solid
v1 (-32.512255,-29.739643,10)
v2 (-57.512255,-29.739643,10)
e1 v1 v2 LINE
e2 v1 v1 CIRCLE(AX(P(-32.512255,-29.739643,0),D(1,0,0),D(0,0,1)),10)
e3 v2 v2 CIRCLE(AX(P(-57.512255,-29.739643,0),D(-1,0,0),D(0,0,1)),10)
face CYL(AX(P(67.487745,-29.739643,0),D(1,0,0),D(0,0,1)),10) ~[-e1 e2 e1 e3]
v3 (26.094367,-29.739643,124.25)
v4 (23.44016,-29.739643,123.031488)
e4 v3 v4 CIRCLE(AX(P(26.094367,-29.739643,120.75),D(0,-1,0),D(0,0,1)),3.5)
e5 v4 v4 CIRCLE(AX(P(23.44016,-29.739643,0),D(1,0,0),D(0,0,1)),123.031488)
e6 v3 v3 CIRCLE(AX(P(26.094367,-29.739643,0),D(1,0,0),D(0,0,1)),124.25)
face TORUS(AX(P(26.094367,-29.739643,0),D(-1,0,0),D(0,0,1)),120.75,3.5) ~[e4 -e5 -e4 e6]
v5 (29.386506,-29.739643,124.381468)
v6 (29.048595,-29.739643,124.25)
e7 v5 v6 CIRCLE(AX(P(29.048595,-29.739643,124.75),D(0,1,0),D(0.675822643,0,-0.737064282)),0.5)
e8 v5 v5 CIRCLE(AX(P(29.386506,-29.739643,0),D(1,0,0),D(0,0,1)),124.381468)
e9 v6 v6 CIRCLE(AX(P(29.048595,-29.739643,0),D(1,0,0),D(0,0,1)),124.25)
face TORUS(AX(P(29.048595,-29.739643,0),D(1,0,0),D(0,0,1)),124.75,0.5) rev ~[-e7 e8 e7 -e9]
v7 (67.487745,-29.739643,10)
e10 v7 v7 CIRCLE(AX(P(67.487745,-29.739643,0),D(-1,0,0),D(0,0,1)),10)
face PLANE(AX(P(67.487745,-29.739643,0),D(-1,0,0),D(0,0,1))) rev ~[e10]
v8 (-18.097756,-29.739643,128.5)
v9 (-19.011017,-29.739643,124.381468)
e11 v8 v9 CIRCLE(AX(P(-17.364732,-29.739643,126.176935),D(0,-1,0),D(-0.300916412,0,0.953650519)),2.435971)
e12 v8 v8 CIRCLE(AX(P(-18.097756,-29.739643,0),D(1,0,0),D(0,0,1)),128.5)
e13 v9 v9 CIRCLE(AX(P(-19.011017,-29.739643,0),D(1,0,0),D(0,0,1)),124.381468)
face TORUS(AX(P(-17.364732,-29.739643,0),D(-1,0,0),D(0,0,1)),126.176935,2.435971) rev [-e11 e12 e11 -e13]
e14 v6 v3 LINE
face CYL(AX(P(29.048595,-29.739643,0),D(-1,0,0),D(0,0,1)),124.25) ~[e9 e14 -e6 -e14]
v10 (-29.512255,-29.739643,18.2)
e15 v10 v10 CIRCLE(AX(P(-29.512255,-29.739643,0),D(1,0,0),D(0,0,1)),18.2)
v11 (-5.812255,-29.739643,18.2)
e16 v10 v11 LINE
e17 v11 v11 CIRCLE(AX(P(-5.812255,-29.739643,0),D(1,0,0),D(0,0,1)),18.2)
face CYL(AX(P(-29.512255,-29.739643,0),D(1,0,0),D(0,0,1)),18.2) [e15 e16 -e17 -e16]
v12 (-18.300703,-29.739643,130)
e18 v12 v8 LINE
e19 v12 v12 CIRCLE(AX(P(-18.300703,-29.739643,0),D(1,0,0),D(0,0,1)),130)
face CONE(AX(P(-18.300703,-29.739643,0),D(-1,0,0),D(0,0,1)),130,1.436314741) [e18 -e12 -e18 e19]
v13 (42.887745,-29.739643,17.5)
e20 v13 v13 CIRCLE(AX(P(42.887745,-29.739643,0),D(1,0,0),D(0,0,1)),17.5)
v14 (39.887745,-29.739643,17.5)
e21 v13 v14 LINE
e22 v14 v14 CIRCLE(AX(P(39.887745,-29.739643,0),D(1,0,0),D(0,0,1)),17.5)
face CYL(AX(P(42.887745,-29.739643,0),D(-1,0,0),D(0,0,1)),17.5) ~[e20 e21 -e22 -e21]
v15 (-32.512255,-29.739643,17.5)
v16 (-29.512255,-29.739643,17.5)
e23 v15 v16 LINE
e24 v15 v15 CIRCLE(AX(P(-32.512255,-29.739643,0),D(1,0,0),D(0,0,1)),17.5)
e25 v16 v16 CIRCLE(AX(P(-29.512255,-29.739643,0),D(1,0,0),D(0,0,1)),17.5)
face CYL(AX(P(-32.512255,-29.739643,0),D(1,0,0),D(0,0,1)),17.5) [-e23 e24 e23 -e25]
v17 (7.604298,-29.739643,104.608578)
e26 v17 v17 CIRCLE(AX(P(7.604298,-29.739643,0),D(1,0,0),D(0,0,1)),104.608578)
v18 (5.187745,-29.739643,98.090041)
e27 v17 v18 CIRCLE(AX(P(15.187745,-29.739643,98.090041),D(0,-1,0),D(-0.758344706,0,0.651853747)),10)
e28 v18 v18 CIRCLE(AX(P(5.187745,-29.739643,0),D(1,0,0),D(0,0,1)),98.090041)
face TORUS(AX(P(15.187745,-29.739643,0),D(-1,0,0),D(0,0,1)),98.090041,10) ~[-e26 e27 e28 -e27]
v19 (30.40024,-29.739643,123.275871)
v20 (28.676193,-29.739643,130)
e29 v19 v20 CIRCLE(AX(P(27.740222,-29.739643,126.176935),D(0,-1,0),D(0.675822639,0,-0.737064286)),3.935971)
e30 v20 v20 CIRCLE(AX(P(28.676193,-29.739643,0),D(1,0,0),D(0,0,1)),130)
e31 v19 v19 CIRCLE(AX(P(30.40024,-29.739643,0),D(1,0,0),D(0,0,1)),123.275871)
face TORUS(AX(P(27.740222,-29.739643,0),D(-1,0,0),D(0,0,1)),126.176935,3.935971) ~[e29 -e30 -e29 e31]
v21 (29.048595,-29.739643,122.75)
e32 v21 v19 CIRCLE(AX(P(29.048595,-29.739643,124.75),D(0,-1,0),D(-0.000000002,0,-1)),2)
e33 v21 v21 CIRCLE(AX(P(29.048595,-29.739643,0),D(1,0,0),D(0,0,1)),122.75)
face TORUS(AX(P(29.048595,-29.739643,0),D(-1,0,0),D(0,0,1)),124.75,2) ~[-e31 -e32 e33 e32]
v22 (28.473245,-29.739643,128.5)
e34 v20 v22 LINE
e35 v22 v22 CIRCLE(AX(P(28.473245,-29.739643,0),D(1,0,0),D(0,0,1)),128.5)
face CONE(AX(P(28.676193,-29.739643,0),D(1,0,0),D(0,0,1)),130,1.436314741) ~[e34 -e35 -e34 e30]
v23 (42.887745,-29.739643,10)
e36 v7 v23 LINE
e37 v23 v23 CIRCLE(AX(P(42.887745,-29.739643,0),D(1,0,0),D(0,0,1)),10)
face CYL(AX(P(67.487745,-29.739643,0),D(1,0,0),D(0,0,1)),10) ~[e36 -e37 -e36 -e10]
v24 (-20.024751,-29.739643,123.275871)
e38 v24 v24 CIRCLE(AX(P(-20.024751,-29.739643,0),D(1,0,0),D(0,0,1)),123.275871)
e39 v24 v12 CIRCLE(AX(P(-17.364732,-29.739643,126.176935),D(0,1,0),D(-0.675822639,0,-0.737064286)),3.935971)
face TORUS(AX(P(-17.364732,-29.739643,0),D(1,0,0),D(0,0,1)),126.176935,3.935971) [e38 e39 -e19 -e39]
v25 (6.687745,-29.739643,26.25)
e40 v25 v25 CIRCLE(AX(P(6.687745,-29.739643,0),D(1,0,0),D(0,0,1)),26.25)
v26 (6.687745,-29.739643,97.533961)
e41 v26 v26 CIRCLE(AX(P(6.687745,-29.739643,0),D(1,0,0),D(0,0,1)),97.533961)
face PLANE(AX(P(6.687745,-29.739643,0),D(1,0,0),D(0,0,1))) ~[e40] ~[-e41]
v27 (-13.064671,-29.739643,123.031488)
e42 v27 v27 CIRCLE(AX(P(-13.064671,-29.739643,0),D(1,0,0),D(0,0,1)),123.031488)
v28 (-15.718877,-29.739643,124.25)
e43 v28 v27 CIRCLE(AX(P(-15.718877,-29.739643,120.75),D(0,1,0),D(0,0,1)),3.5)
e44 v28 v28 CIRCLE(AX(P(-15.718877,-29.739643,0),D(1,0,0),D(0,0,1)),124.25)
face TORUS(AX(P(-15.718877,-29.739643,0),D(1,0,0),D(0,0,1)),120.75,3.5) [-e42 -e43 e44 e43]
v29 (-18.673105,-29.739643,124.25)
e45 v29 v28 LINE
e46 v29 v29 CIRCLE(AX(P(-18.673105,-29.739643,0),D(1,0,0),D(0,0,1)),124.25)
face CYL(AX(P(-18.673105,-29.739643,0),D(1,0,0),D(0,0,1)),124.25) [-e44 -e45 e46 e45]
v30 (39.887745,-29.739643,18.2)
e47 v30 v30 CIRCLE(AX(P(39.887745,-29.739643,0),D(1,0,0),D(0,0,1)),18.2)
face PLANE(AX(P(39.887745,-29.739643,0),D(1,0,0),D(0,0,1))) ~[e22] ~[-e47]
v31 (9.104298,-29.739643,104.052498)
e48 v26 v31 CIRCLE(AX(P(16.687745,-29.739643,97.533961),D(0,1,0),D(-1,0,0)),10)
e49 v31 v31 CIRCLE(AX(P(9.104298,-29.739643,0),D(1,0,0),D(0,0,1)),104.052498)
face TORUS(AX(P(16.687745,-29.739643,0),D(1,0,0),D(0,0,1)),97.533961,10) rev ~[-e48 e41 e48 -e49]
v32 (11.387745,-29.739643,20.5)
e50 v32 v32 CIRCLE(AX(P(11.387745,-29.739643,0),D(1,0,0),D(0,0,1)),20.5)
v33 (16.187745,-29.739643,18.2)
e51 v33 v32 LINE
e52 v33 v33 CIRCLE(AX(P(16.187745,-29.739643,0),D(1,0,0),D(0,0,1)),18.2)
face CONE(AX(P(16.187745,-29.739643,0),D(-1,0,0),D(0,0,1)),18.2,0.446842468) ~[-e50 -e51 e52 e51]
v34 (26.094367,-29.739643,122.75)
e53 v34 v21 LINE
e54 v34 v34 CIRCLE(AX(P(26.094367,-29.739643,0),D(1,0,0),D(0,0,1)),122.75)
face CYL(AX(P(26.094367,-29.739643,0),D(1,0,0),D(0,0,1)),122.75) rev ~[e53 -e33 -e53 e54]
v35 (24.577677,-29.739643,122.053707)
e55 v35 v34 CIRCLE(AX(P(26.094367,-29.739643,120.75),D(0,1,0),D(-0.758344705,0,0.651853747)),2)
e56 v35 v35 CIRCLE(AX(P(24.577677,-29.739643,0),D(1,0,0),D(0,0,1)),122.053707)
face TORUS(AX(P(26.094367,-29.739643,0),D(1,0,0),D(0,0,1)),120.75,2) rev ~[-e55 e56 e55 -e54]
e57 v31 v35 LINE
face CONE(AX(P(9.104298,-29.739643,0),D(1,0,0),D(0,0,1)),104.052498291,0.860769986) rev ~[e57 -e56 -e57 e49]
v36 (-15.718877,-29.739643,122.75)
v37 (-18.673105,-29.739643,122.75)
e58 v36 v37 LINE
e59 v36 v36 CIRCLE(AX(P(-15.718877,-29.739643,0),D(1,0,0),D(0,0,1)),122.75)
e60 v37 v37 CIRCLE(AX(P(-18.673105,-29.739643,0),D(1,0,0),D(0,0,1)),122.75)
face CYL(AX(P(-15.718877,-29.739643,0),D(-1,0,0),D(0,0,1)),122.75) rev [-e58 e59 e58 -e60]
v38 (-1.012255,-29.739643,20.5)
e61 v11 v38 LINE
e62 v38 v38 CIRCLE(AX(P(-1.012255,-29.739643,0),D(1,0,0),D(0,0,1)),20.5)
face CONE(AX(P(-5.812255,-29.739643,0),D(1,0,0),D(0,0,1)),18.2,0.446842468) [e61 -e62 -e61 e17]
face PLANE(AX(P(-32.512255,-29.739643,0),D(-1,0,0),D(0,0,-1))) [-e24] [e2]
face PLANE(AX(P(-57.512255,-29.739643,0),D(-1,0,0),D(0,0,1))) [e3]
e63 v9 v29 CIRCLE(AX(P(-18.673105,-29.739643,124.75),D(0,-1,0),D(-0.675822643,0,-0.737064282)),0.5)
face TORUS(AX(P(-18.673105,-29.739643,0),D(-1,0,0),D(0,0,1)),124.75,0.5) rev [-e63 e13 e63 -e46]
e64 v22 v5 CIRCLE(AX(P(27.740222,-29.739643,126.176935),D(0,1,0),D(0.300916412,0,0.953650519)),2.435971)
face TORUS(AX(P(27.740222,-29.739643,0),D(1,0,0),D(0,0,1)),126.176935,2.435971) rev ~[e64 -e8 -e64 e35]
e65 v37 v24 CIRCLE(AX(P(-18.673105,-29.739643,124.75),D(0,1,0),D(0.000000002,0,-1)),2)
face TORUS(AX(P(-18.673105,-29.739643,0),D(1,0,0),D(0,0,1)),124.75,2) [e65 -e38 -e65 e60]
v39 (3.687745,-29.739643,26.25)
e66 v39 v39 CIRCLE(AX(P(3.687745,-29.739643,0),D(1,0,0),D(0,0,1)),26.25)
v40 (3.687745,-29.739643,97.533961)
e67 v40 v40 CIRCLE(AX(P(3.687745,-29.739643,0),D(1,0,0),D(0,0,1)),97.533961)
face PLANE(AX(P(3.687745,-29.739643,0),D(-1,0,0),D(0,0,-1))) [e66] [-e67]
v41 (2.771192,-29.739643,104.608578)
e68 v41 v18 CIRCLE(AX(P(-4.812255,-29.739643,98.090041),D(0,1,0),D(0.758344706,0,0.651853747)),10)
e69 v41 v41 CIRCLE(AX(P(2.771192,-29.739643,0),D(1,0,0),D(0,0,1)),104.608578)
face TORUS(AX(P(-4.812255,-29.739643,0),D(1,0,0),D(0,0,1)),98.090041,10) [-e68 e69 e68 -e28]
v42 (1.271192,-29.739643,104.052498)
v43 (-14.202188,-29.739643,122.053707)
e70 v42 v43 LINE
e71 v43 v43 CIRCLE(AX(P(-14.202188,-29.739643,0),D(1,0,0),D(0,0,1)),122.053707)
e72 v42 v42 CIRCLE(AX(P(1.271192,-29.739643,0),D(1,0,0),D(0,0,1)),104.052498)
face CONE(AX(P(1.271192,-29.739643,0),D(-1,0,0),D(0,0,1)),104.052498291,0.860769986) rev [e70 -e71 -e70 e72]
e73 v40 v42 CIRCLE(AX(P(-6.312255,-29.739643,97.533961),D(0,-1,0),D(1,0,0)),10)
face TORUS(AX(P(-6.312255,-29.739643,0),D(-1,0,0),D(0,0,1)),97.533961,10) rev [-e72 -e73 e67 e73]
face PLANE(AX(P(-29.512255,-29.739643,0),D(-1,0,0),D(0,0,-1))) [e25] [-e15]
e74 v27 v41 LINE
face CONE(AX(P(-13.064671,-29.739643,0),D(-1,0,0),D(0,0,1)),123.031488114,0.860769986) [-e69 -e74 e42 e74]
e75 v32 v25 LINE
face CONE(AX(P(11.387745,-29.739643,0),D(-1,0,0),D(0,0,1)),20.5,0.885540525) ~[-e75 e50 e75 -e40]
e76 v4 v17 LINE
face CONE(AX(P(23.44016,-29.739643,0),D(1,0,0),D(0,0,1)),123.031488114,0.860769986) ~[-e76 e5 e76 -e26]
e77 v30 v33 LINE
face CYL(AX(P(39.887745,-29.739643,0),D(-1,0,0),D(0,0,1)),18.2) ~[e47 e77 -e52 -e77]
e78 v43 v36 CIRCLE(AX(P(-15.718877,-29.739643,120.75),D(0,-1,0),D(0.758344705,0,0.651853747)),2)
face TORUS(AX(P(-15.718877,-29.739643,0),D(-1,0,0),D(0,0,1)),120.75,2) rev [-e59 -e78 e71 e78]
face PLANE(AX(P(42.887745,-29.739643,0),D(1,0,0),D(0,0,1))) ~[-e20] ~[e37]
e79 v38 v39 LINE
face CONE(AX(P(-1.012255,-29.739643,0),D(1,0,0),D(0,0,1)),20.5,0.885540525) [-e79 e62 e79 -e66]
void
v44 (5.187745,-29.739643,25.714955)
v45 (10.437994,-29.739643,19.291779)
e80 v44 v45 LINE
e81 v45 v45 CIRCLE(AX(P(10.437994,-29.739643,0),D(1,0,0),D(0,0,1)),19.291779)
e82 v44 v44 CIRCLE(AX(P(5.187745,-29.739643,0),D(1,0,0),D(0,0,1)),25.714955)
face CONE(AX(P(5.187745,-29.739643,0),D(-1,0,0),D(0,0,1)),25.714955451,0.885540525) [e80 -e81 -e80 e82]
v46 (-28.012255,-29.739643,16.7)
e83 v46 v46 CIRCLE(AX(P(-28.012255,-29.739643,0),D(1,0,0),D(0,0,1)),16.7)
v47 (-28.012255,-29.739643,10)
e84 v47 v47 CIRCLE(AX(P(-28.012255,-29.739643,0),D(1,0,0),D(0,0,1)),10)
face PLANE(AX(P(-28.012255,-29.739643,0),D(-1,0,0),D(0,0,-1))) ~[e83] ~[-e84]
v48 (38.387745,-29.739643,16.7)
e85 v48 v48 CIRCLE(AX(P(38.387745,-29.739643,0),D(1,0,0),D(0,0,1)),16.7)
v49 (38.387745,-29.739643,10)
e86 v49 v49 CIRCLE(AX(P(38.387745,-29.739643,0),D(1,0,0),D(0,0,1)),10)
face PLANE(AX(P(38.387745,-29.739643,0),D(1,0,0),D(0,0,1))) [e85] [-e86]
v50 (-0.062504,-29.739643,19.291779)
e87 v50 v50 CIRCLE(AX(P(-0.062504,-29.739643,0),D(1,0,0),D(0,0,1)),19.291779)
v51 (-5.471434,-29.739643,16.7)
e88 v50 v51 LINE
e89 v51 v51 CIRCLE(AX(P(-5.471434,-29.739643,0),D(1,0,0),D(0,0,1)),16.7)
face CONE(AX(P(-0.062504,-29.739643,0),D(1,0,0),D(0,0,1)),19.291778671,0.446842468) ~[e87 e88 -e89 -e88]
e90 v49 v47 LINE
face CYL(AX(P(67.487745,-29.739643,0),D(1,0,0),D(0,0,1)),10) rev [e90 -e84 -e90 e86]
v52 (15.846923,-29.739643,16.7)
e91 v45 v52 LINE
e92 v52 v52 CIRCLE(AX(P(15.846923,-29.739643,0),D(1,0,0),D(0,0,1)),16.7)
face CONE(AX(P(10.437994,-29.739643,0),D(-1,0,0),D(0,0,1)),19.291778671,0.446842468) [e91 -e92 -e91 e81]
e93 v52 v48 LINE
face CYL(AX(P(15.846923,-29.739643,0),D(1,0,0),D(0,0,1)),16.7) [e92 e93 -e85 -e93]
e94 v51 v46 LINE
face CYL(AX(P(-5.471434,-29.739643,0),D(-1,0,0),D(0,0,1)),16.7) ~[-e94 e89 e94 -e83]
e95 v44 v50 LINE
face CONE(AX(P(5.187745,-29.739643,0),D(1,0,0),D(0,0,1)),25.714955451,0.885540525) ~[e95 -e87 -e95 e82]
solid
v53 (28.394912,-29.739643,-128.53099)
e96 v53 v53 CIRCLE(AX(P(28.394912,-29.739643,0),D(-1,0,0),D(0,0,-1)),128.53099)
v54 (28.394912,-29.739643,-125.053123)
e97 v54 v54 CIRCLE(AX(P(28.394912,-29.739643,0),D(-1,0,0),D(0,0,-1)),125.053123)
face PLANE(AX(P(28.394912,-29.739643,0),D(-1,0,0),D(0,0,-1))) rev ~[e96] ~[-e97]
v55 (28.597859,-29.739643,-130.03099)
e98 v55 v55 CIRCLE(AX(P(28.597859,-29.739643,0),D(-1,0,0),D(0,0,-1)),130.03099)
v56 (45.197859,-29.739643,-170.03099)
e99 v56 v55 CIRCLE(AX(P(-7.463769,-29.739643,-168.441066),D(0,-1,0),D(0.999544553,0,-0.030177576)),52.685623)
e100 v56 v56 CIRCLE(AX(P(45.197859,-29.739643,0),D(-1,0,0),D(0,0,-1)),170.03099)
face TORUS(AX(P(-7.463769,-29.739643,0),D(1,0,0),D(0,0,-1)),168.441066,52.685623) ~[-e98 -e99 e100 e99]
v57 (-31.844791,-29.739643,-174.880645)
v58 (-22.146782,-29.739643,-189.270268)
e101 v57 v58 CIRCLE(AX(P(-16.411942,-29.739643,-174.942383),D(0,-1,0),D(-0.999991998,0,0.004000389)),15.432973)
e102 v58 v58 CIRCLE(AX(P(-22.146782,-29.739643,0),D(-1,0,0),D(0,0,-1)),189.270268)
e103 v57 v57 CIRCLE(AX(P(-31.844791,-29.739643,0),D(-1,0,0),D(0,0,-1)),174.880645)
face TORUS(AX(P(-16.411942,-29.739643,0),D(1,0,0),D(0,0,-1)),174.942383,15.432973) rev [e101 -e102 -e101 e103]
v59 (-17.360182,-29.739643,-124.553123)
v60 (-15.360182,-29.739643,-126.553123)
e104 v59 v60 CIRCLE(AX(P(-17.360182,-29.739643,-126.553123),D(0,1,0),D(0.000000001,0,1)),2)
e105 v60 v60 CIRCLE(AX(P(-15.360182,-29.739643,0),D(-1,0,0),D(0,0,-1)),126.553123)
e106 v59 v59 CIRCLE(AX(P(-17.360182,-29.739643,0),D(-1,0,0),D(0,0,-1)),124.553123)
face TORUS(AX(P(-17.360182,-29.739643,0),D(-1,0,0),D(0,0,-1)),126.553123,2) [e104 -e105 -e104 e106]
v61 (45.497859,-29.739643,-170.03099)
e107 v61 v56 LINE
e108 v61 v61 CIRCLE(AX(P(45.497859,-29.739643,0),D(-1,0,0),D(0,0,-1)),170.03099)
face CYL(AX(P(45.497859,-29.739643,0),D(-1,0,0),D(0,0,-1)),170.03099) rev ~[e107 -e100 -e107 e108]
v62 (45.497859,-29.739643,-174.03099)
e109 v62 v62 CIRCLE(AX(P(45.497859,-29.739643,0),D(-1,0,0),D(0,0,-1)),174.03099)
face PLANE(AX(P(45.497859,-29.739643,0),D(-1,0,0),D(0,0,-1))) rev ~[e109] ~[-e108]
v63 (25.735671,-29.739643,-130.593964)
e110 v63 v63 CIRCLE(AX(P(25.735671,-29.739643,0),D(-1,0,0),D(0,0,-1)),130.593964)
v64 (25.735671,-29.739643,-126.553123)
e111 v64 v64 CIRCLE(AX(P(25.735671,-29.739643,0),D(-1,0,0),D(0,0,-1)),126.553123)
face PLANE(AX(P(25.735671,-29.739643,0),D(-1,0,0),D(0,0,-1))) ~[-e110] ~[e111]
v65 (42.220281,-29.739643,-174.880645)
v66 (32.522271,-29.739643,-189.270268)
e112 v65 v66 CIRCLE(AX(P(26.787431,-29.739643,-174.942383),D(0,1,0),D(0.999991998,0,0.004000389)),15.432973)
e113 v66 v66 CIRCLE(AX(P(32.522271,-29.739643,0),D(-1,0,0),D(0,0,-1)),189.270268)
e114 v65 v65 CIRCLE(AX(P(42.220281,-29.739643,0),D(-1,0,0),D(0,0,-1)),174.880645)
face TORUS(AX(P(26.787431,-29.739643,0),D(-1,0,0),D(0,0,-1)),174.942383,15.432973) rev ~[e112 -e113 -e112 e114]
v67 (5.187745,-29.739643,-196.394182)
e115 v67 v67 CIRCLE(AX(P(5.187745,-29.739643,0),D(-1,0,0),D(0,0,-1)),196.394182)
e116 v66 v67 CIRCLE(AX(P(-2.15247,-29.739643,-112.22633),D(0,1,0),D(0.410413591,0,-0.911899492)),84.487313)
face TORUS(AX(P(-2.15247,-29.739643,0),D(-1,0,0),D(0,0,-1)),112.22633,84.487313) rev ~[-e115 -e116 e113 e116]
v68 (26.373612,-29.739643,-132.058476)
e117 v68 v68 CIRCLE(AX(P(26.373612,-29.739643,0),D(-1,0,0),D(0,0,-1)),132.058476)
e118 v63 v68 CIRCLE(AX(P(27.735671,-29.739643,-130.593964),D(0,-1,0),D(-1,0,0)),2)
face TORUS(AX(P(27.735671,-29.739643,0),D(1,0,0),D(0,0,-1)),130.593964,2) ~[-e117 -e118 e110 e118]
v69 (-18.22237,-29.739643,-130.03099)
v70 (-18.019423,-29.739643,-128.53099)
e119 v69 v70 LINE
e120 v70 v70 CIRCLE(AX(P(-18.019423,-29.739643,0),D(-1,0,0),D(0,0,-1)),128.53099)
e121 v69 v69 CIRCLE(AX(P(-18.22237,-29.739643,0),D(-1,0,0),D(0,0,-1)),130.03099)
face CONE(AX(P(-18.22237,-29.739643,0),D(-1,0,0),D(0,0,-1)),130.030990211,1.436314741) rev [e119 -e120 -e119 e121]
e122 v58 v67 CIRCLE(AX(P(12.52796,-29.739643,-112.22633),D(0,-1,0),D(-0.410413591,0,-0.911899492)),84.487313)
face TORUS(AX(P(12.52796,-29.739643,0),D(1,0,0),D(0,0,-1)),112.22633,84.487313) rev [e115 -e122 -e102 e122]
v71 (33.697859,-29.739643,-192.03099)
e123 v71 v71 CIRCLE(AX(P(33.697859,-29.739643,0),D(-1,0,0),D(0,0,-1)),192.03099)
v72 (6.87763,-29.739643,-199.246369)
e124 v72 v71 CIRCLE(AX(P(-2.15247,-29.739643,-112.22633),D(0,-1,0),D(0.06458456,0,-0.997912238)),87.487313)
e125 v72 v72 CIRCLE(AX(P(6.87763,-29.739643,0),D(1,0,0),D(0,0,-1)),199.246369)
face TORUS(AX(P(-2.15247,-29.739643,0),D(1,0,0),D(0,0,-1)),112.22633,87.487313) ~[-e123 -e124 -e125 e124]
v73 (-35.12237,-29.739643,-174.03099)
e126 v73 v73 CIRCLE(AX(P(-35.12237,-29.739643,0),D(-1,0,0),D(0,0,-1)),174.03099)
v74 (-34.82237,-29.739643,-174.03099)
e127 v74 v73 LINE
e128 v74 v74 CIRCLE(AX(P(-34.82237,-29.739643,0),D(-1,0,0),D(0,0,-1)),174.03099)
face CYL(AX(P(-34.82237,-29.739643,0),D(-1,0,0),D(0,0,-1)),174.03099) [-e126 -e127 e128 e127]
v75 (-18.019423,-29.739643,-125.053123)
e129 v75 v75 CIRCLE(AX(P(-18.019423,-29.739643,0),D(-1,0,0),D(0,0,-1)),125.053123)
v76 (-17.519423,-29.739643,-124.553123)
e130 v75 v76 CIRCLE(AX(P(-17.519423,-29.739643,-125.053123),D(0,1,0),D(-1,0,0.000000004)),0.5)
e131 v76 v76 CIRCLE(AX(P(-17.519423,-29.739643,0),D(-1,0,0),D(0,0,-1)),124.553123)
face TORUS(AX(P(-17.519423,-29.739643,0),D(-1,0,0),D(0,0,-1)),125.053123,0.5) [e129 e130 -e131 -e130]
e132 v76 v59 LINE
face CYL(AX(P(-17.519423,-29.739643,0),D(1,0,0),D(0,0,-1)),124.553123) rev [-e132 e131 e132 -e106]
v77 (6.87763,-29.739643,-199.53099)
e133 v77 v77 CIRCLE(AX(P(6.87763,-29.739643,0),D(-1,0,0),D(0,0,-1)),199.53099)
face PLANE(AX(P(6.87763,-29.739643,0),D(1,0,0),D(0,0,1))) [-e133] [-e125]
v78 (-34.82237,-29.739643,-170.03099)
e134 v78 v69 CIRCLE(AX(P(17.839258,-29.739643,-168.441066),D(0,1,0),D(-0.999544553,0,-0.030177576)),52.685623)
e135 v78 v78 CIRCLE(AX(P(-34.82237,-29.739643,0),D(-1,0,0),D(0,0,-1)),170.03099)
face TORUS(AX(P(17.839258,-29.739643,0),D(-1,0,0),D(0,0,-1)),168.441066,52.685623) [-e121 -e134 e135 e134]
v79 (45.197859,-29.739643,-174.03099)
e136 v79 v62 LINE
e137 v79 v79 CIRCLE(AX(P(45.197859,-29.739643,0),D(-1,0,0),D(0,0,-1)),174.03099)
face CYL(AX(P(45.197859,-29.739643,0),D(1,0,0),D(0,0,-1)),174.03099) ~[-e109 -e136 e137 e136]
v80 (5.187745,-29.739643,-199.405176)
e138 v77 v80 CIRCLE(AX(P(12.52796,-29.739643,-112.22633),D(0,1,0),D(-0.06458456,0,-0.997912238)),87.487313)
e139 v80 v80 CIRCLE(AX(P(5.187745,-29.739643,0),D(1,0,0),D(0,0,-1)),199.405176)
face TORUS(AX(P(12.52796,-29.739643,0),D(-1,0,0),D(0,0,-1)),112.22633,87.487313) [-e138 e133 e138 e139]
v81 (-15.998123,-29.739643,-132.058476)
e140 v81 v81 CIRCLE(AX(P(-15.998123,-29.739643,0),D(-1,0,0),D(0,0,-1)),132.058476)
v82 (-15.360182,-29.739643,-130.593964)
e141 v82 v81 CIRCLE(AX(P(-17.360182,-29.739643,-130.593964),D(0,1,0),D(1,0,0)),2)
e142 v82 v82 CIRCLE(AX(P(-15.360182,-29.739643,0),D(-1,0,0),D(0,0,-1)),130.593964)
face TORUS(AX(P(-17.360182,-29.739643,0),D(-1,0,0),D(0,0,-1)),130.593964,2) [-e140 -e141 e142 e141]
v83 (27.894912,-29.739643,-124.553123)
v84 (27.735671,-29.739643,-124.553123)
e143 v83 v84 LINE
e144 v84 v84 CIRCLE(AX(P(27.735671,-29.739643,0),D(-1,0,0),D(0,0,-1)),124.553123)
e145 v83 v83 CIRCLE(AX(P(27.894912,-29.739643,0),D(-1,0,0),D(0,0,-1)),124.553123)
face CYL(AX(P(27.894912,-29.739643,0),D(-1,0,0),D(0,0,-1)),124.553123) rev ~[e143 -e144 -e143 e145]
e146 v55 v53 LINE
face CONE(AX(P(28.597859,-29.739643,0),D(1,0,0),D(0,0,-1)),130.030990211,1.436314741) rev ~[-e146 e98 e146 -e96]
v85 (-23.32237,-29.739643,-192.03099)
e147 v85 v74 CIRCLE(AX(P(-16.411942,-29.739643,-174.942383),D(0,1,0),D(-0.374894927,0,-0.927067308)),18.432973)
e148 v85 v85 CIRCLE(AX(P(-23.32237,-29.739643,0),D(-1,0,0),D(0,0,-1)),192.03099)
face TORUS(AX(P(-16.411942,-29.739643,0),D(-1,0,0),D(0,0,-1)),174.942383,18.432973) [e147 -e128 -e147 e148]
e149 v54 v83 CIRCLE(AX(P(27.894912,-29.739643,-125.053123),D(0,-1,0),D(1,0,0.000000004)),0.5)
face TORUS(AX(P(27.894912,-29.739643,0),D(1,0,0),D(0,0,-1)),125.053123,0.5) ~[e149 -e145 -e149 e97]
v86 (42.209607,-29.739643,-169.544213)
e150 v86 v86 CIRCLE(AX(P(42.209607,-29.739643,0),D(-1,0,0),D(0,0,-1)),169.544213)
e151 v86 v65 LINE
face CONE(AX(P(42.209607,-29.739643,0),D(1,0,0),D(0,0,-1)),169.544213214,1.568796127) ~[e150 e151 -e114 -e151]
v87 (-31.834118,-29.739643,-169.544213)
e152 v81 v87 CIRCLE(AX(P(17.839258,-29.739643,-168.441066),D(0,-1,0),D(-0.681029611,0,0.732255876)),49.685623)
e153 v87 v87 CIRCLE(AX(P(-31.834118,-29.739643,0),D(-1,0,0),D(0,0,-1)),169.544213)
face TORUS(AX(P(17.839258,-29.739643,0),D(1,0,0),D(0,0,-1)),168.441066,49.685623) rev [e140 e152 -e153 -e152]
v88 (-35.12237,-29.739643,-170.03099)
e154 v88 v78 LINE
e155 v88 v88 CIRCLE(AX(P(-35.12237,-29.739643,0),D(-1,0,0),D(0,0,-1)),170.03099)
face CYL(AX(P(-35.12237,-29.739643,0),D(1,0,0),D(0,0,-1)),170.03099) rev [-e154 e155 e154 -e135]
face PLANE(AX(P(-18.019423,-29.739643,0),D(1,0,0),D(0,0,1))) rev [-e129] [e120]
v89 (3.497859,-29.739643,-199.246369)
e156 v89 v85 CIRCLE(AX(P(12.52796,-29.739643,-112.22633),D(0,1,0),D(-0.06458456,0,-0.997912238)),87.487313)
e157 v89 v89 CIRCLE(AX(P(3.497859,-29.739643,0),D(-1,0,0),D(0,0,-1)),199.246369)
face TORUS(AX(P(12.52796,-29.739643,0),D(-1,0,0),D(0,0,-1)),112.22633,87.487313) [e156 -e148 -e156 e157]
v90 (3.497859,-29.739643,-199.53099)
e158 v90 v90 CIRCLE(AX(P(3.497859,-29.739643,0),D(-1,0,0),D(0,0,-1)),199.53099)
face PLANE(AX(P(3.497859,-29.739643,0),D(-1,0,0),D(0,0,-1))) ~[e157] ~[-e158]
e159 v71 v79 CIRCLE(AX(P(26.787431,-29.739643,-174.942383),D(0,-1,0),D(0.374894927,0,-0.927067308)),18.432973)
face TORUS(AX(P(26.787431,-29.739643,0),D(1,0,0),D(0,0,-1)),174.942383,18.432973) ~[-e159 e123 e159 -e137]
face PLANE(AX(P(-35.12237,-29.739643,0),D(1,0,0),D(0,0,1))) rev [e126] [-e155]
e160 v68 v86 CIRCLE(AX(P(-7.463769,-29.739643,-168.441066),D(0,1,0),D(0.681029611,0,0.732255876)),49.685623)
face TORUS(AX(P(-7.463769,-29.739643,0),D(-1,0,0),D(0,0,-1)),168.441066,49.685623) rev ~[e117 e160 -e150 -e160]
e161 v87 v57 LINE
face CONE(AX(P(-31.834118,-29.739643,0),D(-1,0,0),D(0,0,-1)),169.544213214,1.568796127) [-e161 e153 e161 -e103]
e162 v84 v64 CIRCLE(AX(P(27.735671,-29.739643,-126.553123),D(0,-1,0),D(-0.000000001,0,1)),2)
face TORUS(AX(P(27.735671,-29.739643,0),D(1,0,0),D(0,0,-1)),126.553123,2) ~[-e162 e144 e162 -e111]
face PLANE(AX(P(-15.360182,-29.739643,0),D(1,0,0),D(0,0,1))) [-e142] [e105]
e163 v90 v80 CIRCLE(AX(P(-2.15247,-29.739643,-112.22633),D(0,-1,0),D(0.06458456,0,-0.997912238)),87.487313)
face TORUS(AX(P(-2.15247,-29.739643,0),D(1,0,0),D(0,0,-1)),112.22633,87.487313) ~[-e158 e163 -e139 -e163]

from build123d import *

# Parameters (mm, degrees)
BOSS_EXTRUDE1_DEPTH      = 25
BOSS_EXTRUDE1_DEPTH_BACK = 100
SKETCH3_R                = 10


with BuildPart() as part:
    # Sketch1 → Revolve1 (revolve)
    with BuildSketch(Plane.XY, mode=Mode.PRIVATE) as revolve1_sk:
        with BuildLine():
            Line((41.387744688, -19.739643253), (42.887744688, -19.739643253))
            Line((42.887744688, -19.739643253), (42.887744688, -12.239643253))
            Line((42.887744688, -12.239643253), (39.887744688, -12.239643253))
            Line((39.887744688, -12.239643253), (39.887744688, -11.539643253))
            Line((39.887744688, -11.539643253), (16.187744688, -11.539643253))
            Line((16.187744688, -11.539643253), (11.387744688, -9.239643253))
            Line((11.387744688, -9.239643253), (6.687744688, -3.489643253))
            Line((6.687744688, -3.489643253), (6.687744688, 67.794317568))
            ThreePointArc((6.687744688, 67.794317568), (7.31132558, 71.270344714), (9.104297631, 74.312855038))
            Line((9.104297631, 74.312855038), (24.577677456, 92.314064241))
            ThreePointArc((24.577677456, 92.314064241), (25.259925434, 92.827967127), (26.094366868, 93.010356747))
            Line((26.094366868, 93.010356747), (29.048594764, 93.010356747))
            ThreePointArc((29.048594764, 93.010356747), (29.773764695, 93.146455308), (30.400240041, 93.536228175))
            ThreePointArc((30.400240041, 93.536228175), (31.552866637, 97.414843022), (28.676192717, 100.260356747))
            Line((28.676192717, 100.260356747), (28.473245406, 98.760356747))
            ThreePointArc((28.473245406, 98.760356747), (30.118425574, 96.964644724), (29.386506083, 94.641824604))
            ThreePointArc((29.386506083, 94.641824604), (29.229887247, 94.544381387), (29.048594764, 94.510356747))
            Line((29.048594764, 94.510356747), (26.094366868, 94.510356747))
            ThreePointArc((26.094366868, 94.510356747), (24.634094359, 94.191174912), (23.440160398, 93.291844861))
            Line((23.440160398, 93.291844861), (7.604297631, 74.868935207))
            ThreePointArc((7.604297631, 74.868935207), (5.81132558, 71.826424883), (5.187744688, 68.350397737))
            Line((5.187744688, 68.350397737), (5.187744688, -4.024687802))
            Line((5.187744688, -4.024687802), (10.437993534, -10.447864582))
            Line((10.437993534, -10.447864582), (15.846922936, -13.039643253))
            Line((15.846922936, -13.039643253), (38.387744688, -13.039643253))
            Line((38.387744688, -13.039643253), (38.387744688, -13.739643253))
            Line((38.387744688, -13.739643253), (38.387744688, -19.739643253))
            Line((38.387744688, -19.739643253), (41.387744688, -19.739643253))
        make_face()
    revolve(revolve1_sk.sketch.rotate(Axis((-118.954757241, -29.739643253, 0), (1, 0, 0)), 90), axis=Axis((-118.954757241, -29.739643253, 0), (1, 0, 0)))


with BuildPart() as body_2:
    # Sketch2 → Revolve2 (revolve)
    with BuildSketch(Plane.XY, mode=Mode.PRIVATE) as revolve2_sk:
        with BuildLine():
            Line((28.597859248, 100.291346958), (28.394911937, 98.791346958))
            Line((28.394911937, 98.791346958), (28.394911937, 95.313479471))
            ThreePointArc((28.394911937, 95.313479471), (28.248465327, 94.959926081), (27.894911937, 94.813479471))
            Line((27.894911937, 94.813479471), (27.735671368, 94.813479471))
            ThreePointArc((27.735671368, 94.813479471), (26.321457806, 95.399265909), (25.735671368, 96.813479471))
            Line((25.735671368, 96.813479471), (25.735671368, 100.854321086))
            ThreePointArc((25.735671368, 100.854321086), (25.902079477, 101.653033035), (26.373612145, 102.318832838))
            ThreePointArc((26.373612145, 102.318832838), (38.305289981, 119.366106553), (42.209606894, 139.804569961))
            Line((42.209606894, 139.804569961), (42.22028084, 145.141002184))
            ThreePointArc((42.22028084, 145.141002184), (39.585207528, 153.827911455), (32.522271283, 159.530624463))
            ThreePointArc((32.522271283, 159.530624463), (18.333714714, 164.452669108), (3.497859248, 166.784846971))
            Line((3.497859248, 166.784846971), (3.497859248, 169.791346958))
            ThreePointArc((3.497859248, 169.791346958), (18.933986878, 167.39482088), (33.697859248, 162.291346958))
            ThreePointArc((33.697859248, 162.291346958), (42.320828696, 155.126855217), (45.197859248, 144.291346958))
            Line((45.197859248, 144.291346958), (45.497859248, 144.291346958))
            Line((45.497859248, 144.291346958), (45.497859248, 140.291346958))
            Line((45.497859248, 140.291346958), (45.197859248, 140.291346958))
            ThreePointArc((45.197859248, 140.291346958), (41.197859248, 118.506846958), (28.597859248, 100.291346958))
        make_face()
    revolve(revolve2_sk.sketch.rotate(Axis((51.301478022, -29.739643253, 0), (-1, 0, 0)), 90), axis=Axis((51.301478022, -29.739643253, 0), (-1, 0, 0)))


with BuildPart() as body_3:
    # Mirror8: mirrored copy
    add(part.part.mirror(Plane(origin=(5.187744688, -4.024687802, 0), x_dir=(0, 0, 1), z_dir=(1, 0, 0))))


with BuildPart() as body_4:
    # Mirror8 2: mirrored copy
    add(body_2.part.mirror(Plane(origin=(5.187744688, -4.024687802, 0), x_dir=(0, 0, 1), z_dir=(1, 0, 0))))


with BuildPart() as part_1:
    add(part.part)

    add(body_3.part)  # Boss-Extrude1 merges body 3

    add(body_2.part)  # Boss-Extrude1 merges body 2

    add(body_4.part)  # Boss-Extrude1 merges body 4
    # Sketch3 → Boss-Extrude1 (add, two sides: drawn at the far end of the back side and taken through both)
    with BuildSketch(Plane.ZY.offset(32.512255312).offset(-BOSS_EXTRUDE1_DEPTH_BACK)):
        with Locations((0, -29.739643253)):
            Circle(SKETCH3_R)
    extrude(amount=BOSS_EXTRUDE1_DEPTH + BOSS_EXTRUDE1_DEPTH_BACK)


solid = part_1.part
